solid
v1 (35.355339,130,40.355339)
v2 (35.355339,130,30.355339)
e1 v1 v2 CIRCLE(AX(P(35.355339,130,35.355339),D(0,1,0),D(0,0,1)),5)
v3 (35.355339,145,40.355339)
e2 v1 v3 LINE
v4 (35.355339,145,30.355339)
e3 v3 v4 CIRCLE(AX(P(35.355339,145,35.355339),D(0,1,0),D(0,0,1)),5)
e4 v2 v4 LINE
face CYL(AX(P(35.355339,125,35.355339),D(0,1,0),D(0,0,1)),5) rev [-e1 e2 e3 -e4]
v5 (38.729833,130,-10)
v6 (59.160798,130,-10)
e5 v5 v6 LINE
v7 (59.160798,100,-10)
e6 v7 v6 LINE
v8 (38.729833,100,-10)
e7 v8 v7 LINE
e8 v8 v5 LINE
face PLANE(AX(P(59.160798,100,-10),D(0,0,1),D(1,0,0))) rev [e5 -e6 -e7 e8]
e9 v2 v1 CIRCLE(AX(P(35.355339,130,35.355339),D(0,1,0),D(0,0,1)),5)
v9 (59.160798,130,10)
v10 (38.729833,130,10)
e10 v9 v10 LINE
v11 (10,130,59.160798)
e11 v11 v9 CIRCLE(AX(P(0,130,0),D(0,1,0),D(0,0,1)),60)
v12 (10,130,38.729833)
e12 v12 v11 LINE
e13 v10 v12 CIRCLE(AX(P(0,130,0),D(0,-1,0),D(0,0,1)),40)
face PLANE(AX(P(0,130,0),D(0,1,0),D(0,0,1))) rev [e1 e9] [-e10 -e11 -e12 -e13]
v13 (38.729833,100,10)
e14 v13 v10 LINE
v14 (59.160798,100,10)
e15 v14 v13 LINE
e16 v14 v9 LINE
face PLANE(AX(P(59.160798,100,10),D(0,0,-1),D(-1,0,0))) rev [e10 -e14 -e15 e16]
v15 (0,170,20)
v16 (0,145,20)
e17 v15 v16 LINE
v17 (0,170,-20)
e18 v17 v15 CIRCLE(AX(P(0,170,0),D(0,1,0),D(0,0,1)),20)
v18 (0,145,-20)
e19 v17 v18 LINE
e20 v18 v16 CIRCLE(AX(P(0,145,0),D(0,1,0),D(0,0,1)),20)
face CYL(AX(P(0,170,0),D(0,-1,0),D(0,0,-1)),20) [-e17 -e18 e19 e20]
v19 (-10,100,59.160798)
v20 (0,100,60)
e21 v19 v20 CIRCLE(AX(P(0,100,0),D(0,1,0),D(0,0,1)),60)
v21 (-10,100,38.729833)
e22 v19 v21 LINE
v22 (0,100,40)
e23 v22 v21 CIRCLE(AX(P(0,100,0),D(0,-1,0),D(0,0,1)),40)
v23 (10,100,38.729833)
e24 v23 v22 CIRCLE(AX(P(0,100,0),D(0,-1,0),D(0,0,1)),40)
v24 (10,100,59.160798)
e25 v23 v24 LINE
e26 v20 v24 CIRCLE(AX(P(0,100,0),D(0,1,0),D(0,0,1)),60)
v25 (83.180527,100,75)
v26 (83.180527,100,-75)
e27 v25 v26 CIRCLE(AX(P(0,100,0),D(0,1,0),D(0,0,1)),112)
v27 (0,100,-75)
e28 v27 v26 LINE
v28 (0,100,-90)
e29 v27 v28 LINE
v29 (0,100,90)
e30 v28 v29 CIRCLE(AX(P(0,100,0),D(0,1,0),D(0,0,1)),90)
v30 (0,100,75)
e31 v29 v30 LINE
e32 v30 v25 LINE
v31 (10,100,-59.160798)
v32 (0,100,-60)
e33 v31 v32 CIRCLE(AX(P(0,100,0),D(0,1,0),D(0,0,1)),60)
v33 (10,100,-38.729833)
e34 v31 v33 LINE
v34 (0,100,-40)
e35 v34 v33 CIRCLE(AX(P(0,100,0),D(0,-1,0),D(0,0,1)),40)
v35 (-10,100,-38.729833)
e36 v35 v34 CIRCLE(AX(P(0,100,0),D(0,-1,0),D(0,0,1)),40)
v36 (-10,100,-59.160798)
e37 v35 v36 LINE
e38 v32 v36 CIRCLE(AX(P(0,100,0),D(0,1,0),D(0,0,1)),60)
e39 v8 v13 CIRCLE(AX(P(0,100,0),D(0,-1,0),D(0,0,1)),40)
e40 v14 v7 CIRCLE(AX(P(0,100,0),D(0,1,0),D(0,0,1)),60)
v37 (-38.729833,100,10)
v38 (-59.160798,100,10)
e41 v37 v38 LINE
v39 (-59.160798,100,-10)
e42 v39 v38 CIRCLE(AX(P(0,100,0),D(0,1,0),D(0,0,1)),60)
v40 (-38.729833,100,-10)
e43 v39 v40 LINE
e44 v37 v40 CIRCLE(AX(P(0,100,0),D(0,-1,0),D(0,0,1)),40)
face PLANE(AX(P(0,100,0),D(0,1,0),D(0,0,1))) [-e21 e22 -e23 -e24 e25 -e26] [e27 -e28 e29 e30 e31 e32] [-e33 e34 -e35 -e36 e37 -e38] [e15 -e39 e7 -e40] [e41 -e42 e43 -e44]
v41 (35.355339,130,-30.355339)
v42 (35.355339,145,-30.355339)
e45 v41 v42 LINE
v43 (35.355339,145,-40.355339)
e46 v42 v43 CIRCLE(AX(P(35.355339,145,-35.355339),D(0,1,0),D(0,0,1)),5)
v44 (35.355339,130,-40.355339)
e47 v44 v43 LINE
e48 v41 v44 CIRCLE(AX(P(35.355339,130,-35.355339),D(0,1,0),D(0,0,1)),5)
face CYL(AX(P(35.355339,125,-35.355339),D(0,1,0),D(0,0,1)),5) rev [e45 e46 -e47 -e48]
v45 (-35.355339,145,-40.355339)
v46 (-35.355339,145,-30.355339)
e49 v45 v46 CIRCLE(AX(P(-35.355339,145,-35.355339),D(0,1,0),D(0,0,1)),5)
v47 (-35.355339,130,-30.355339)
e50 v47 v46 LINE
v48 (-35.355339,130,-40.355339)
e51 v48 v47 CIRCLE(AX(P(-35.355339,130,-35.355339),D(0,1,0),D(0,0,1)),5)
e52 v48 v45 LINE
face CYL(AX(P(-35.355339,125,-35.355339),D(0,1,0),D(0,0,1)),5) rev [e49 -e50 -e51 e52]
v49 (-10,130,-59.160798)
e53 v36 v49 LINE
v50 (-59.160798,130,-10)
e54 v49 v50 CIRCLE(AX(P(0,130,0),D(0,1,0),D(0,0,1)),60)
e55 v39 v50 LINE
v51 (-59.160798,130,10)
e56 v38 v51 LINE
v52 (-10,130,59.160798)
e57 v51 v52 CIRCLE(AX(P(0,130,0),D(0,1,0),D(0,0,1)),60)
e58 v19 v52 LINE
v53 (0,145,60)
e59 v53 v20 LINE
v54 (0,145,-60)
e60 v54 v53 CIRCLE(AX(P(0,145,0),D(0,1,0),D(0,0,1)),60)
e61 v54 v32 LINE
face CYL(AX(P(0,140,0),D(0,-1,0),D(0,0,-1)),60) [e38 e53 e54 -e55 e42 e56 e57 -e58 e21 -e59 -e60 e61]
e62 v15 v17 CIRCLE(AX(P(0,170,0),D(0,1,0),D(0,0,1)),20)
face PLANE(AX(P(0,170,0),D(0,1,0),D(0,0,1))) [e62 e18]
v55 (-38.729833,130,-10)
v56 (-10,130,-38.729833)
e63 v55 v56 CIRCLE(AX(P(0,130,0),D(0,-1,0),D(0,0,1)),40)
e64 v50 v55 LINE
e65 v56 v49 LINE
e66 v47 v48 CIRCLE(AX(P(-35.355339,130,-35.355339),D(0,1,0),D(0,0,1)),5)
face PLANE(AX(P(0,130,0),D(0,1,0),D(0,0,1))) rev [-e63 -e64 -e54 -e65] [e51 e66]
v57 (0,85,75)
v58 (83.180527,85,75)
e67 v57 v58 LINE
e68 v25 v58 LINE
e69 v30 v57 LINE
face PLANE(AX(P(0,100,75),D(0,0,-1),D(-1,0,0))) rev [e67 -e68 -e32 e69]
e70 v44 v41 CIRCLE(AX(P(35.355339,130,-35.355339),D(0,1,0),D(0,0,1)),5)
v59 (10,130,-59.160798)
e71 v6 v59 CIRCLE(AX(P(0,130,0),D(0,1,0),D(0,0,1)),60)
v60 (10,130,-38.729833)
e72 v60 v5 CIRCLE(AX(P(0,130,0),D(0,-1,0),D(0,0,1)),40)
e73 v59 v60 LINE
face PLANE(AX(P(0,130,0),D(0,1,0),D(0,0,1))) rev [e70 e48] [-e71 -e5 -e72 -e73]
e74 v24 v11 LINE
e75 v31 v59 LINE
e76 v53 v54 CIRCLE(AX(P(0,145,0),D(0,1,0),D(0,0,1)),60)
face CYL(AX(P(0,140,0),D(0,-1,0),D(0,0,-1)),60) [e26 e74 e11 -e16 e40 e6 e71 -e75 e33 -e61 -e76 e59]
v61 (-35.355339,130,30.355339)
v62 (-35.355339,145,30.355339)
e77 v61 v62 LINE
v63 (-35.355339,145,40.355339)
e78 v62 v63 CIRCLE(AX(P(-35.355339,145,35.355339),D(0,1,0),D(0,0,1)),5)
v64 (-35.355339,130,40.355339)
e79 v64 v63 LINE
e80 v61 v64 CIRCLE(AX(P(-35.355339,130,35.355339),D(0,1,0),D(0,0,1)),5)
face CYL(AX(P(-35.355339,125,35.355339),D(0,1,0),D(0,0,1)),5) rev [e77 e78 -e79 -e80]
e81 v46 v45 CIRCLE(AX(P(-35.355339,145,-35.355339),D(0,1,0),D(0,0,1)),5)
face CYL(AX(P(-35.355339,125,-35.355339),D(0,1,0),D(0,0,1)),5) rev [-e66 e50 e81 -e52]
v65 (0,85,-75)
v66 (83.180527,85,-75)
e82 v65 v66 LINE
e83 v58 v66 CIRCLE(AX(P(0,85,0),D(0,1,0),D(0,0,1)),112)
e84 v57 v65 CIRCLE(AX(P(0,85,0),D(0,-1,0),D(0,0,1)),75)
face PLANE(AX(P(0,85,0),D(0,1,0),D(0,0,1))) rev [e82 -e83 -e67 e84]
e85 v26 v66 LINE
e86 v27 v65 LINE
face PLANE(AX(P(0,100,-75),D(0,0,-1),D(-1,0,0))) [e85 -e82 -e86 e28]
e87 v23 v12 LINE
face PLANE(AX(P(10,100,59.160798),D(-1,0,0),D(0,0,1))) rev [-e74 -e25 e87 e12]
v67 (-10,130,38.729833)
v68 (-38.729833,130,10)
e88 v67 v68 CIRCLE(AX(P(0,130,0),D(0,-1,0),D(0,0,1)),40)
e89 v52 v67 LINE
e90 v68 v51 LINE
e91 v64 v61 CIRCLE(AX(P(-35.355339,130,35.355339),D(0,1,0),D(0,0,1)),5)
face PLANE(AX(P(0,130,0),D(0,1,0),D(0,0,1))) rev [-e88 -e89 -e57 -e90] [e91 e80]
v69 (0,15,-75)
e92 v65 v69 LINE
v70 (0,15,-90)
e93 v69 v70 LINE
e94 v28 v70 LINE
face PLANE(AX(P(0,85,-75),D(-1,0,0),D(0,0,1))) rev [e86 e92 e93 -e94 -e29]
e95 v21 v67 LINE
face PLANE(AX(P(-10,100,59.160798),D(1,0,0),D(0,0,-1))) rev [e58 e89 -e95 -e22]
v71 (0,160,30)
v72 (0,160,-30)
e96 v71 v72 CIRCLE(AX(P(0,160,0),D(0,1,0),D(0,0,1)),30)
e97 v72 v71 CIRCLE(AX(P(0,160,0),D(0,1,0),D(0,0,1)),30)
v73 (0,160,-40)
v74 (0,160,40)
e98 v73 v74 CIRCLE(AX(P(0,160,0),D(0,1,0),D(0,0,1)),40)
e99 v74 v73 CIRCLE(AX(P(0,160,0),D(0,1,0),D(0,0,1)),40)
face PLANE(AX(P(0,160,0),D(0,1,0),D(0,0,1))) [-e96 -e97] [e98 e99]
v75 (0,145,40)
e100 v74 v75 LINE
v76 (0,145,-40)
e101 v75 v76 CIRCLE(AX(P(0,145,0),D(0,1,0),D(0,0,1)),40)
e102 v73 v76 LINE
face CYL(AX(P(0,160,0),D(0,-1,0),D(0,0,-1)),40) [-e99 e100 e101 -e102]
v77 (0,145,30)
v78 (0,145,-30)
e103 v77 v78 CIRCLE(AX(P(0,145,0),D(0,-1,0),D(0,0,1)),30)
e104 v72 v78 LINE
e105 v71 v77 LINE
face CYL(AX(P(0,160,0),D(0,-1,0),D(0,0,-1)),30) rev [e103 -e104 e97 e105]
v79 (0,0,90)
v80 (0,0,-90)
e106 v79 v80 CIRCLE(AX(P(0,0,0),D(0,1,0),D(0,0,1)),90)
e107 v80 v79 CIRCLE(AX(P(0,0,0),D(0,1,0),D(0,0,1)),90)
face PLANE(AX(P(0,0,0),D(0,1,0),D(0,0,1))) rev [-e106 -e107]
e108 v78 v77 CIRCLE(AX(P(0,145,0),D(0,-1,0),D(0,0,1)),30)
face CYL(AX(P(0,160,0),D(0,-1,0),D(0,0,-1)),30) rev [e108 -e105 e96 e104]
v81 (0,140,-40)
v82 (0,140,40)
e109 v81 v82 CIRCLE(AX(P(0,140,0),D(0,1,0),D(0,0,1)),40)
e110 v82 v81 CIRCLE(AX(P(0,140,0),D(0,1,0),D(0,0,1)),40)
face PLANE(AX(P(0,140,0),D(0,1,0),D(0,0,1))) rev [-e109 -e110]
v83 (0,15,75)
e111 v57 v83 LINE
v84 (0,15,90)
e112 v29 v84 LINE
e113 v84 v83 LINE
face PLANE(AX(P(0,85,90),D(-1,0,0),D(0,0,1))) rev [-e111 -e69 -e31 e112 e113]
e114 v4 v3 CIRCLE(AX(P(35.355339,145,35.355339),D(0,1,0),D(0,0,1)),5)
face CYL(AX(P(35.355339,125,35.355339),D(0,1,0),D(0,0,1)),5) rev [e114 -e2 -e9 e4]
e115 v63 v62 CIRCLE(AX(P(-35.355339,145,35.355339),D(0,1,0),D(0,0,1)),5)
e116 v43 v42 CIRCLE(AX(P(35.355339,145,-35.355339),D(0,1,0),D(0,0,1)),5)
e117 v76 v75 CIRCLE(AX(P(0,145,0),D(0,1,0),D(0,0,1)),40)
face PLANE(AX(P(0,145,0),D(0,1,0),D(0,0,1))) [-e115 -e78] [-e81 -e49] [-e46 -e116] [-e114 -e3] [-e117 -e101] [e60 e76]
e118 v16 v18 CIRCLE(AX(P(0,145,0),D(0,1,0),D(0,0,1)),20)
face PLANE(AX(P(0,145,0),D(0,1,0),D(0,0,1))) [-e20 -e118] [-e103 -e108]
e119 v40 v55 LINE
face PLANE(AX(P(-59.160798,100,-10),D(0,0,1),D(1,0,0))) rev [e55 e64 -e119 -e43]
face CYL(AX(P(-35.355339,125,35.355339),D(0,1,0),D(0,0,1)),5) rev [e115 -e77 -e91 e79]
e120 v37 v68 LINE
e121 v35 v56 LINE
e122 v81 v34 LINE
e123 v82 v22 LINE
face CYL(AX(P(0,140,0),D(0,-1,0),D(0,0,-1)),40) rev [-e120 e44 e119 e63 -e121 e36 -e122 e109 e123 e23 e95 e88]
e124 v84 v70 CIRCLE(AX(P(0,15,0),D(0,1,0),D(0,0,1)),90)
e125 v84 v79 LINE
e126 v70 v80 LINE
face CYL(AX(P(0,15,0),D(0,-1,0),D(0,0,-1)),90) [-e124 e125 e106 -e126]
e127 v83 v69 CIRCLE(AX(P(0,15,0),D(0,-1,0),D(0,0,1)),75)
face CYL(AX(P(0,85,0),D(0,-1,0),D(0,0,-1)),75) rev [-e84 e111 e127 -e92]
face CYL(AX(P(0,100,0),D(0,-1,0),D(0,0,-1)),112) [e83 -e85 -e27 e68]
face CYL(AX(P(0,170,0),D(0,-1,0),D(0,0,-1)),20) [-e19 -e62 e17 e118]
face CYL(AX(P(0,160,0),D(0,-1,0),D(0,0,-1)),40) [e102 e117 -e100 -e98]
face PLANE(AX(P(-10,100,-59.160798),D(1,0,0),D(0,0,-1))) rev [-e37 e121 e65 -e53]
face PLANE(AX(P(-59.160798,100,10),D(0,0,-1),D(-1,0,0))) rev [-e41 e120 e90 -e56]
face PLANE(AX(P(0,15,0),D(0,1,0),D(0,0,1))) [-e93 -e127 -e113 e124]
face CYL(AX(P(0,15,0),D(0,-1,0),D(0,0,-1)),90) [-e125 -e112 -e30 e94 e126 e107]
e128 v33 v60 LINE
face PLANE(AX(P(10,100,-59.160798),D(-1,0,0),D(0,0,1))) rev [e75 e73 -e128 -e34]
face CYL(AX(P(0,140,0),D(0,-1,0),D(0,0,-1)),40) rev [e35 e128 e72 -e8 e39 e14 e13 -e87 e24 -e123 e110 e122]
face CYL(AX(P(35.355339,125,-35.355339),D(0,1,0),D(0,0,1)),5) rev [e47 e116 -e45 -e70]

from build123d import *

# Parameters (mm, degrees)
BASE_DISC_SKETCH_R           = 90
BASE_DISC_180_DEPTH          = 15
CLAMP_FRAME_WALL_DEPTH       = 70
TOP_JAW_PLATE_DEPTH          = 15
TABLE_RISER_SKETCH_R         = 60
TABLE_RISER_SKETCH_R_2       = 40
TABLE_RISER_DEPTH            = 40
RISER_START                  = -30
RISER_SLOTS_CUT_DEPTH        = 30
TABLE_PLATE_SKETCH_R         = 60
TABLE_PLATE_120_DEPTH        = 5
TABLE_BOLT_HOLES_SKETCH_R    = 5
TABLE_BOLT_HOLES_4X_10_DEPTH = 20
TABLE_RING_SKETCH_R          = 40
TABLE_RING_SKETCH_R_2        = 30
TABLE_RING_80_DEPTH          = 15
CENTRE_SPIGOT_SKETCH_R       = 20
CENTRE_SPIGOT_40_DEPTH       = 25


with BuildPart() as part:
    # Base Disc Sketch → Base Disc Ø180 (new body)
    with BuildSketch(Plane(origin=(0, 0, 0), x_dir=(1, 0, 0), z_dir=(0, 1, 0))):
        with Locations(Location((0, 0, 0), (0, 0, 270))):
            Circle(BASE_DISC_SKETCH_R)
    extrude(amount=BASE_DISC_180_DEPTH)

    # Clamp Frame Wall Sketch → Clamp Frame Wall (add)
    with BuildSketch(Plane(origin=(0, 15, 0), x_dir=(1, 0, 0), z_dir=(0, 1, 0))):
        with BuildLine():
            Line((0, -90), (0, -75))
            ThreePointArc((0, -75), (-75, 0), (0, 75))
            Line((0, 75), (0, 90))
            ThreePointArc((0, 90), (-90, 0), (0, -90))
        make_face()
    extrude(amount=CLAMP_FRAME_WALL_DEPTH)

    # Top Jaw Sketch → Top Jaw Plate (add)
    with BuildSketch(Plane(origin=(0, 85, 0), x_dir=(1, 0, 0), z_dir=(0, 1, 0))):
        with BuildLine():
            Line((0, 75), (0, 90))
            ThreePointArc((0, 90), (-90, 0), (0, -90))
            Line((0, -90), (0, -75))
            ThreePointArc((0, -75), (-75, 0), (0, 75))
        make_face()
        with BuildLine():
            Line((0, -75), (0, 75))
            ThreePointArc((0, 75), (-75, 0), (0, -75))
        make_face()
        with BuildLine():
            Line((83.180526567, 75), (0, 75))
            Line((0, 75), (0, -75))
            Line((0, -75), (49.749371855, -75))
            Line((49.749371855, -75), (83.180526567, -75))
            ThreePointArc((83.180526567, -75), (112, 0), (83.180526567, 75))
        make_face()
    extrude(amount=TOP_JAW_PLATE_DEPTH)

    # Table Riser Sketch → Table Riser (add)
    with BuildSketch(Plane(origin=(0, 100, 0), x_dir=(1, 0, 0), z_dir=(0, 1, 0))):
        with Locations(Location((0, 0, 0), (0, 0, 270))):
            Circle(TABLE_RISER_SKETCH_R)
        with Locations(Location((0, 0, 0), (0, 0, 270))):
            Circle(TABLE_RISER_SKETCH_R_2, mode=Mode.SUBTRACT)
    extrude(amount=TABLE_RISER_DEPTH)

    # Riser Slots Sketch → Riser Slots Cut (cut)
    with BuildSketch(Plane(origin=(0, 130, 0), x_dir=(1, 0, 0), z_dir=(0, 1, 0)).offset(RISER_START)):
        with BuildLine():
            Line((59.160797831, 10), (38.729833462, 10))
            ThreePointArc((38.729833462, 10), (28.284271247, 28.284271247), (10, 38.729833462))
            Line((10, 38.729833462), (10, 59.160797831))
            ThreePointArc((10, 59.160797831), (42.426406871, 42.426406871), (59.160797831, 10))
        make_face()
        with BuildLine():
            Line((-10, 59.160797831), (-10, 38.729833462))
            ThreePointArc((-10, 38.729833462), (-28.284271247, 28.284271247), (-38.729833462, 10))
            Line((-38.729833462, 10), (-59.160797831, 10))
            ThreePointArc((-59.160797831, 10), (-42.426406871, 42.426406871), (-10, 59.160797831))
        make_face()
        with BuildLine():
            Line((59.160797831, -10), (38.729833462, -10))
            ThreePointArc((38.729833462, -10), (28.284271247, -28.284271247), (10, -38.729833462))
            Line((10, -38.729833462), (10, -59.160797831))
            ThreePointArc((10, -59.160797831), (42.426406871, -42.426406871), (59.160797831, -10))
        make_face()
        with BuildLine():
            Line((-10, -59.160797831), (-10, -38.729833462))
            ThreePointArc((-10, -38.729833462), (-28.284271247, -28.284271247), (-38.729833462, -10))
            Line((-38.729833462, -10), (-59.160797831, -10))
            ThreePointArc((-59.160797831, -10), (-42.426406871, -42.426406871), (-10, -59.160797831))
        make_face()
    extrude(amount=RISER_SLOTS_CUT_DEPTH, mode=Mode.SUBTRACT)

    # Table Plate Sketch → Table Plate Ø120 (add)
    with BuildSketch(Plane(origin=(0, 140, 0), x_dir=(1, 0, 0), z_dir=(0, 1, 0))):
        with Locations(Location((0, 0, 0), (0, 0, 80.405931773))):
            Circle(TABLE_PLATE_SKETCH_R)
    extrude(amount=TABLE_PLATE_120_DEPTH)

    # Table Bolt Holes Sketch → Table Bolt Holes 4xØ10 (cut)
    with BuildSketch(Plane(origin=(0, 145, 0), x_dir=(1, 0, 0), z_dir=(0, 1, 0))):
        with BuildLine():
            ThreePointArc((38.890872965, 38.890872965), (31.819805153, 38.890872965), (31.819805153, 31.819805153))
            Line((31.819805153, 31.819805153), (38.890872965, 38.890872965))
        make_face()
        with BuildLine():
            Line((38.890872965, 38.890872965), (31.819805153, 31.819805153))
            ThreePointArc((31.819805153, 31.819805153), (37.268756221, 30.735941397), (40.355339059, 35.355339059))
            ThreePointArc((40.355339059, 35.355339059), (39.974736722, 37.268756221), (38.890872965, 38.890872965))
        make_face()
        with Locations(Location((-35.355339059, 35.355339059, 0), (0, 0, 270))):
            Circle(TABLE_BOLT_HOLES_SKETCH_R)
        with Locations(Location((-35.355339059, -35.355339059, 0), (0, 0, 270))):
            Circle(TABLE_BOLT_HOLES_SKETCH_R)
        with Locations(Location((35.355339059, -35.355339059, 0), (0, 0, 270))):
            Circle(TABLE_BOLT_HOLES_SKETCH_R)
    extrude(amount=-TABLE_BOLT_HOLES_4X_10_DEPTH, mode=Mode.SUBTRACT)

    # Table Ring Sketch → Table Ring Ø80 (add)
    with BuildSketch(Plane(origin=(0, 145, 0), x_dir=(1, 0, 0), z_dir=(0, 1, 0))):
        with Locations(Location((0, 0, 0), (0, 0, 75.522487814))):
            Circle(TABLE_RING_SKETCH_R)
        with Locations(Location((0, 0, 0), (0, 0, 270))):
            Circle(TABLE_RING_SKETCH_R_2, mode=Mode.SUBTRACT)
    extrude(amount=TABLE_RING_80_DEPTH)

    # Centre Spigot Sketch → Centre Spigot Ø40 (add)
    with BuildSketch(Plane(origin=(0, 145, 0), x_dir=(1, 0, 0), z_dir=(0, 1, 0))):
        with Locations(Location((0, 0, 0), (0, 0, 270))):
            Circle(CENTRE_SPIGOT_SKETCH_R)
    extrude(amount=CENTRE_SPIGOT_40_DEPTH)


solid = part.part
